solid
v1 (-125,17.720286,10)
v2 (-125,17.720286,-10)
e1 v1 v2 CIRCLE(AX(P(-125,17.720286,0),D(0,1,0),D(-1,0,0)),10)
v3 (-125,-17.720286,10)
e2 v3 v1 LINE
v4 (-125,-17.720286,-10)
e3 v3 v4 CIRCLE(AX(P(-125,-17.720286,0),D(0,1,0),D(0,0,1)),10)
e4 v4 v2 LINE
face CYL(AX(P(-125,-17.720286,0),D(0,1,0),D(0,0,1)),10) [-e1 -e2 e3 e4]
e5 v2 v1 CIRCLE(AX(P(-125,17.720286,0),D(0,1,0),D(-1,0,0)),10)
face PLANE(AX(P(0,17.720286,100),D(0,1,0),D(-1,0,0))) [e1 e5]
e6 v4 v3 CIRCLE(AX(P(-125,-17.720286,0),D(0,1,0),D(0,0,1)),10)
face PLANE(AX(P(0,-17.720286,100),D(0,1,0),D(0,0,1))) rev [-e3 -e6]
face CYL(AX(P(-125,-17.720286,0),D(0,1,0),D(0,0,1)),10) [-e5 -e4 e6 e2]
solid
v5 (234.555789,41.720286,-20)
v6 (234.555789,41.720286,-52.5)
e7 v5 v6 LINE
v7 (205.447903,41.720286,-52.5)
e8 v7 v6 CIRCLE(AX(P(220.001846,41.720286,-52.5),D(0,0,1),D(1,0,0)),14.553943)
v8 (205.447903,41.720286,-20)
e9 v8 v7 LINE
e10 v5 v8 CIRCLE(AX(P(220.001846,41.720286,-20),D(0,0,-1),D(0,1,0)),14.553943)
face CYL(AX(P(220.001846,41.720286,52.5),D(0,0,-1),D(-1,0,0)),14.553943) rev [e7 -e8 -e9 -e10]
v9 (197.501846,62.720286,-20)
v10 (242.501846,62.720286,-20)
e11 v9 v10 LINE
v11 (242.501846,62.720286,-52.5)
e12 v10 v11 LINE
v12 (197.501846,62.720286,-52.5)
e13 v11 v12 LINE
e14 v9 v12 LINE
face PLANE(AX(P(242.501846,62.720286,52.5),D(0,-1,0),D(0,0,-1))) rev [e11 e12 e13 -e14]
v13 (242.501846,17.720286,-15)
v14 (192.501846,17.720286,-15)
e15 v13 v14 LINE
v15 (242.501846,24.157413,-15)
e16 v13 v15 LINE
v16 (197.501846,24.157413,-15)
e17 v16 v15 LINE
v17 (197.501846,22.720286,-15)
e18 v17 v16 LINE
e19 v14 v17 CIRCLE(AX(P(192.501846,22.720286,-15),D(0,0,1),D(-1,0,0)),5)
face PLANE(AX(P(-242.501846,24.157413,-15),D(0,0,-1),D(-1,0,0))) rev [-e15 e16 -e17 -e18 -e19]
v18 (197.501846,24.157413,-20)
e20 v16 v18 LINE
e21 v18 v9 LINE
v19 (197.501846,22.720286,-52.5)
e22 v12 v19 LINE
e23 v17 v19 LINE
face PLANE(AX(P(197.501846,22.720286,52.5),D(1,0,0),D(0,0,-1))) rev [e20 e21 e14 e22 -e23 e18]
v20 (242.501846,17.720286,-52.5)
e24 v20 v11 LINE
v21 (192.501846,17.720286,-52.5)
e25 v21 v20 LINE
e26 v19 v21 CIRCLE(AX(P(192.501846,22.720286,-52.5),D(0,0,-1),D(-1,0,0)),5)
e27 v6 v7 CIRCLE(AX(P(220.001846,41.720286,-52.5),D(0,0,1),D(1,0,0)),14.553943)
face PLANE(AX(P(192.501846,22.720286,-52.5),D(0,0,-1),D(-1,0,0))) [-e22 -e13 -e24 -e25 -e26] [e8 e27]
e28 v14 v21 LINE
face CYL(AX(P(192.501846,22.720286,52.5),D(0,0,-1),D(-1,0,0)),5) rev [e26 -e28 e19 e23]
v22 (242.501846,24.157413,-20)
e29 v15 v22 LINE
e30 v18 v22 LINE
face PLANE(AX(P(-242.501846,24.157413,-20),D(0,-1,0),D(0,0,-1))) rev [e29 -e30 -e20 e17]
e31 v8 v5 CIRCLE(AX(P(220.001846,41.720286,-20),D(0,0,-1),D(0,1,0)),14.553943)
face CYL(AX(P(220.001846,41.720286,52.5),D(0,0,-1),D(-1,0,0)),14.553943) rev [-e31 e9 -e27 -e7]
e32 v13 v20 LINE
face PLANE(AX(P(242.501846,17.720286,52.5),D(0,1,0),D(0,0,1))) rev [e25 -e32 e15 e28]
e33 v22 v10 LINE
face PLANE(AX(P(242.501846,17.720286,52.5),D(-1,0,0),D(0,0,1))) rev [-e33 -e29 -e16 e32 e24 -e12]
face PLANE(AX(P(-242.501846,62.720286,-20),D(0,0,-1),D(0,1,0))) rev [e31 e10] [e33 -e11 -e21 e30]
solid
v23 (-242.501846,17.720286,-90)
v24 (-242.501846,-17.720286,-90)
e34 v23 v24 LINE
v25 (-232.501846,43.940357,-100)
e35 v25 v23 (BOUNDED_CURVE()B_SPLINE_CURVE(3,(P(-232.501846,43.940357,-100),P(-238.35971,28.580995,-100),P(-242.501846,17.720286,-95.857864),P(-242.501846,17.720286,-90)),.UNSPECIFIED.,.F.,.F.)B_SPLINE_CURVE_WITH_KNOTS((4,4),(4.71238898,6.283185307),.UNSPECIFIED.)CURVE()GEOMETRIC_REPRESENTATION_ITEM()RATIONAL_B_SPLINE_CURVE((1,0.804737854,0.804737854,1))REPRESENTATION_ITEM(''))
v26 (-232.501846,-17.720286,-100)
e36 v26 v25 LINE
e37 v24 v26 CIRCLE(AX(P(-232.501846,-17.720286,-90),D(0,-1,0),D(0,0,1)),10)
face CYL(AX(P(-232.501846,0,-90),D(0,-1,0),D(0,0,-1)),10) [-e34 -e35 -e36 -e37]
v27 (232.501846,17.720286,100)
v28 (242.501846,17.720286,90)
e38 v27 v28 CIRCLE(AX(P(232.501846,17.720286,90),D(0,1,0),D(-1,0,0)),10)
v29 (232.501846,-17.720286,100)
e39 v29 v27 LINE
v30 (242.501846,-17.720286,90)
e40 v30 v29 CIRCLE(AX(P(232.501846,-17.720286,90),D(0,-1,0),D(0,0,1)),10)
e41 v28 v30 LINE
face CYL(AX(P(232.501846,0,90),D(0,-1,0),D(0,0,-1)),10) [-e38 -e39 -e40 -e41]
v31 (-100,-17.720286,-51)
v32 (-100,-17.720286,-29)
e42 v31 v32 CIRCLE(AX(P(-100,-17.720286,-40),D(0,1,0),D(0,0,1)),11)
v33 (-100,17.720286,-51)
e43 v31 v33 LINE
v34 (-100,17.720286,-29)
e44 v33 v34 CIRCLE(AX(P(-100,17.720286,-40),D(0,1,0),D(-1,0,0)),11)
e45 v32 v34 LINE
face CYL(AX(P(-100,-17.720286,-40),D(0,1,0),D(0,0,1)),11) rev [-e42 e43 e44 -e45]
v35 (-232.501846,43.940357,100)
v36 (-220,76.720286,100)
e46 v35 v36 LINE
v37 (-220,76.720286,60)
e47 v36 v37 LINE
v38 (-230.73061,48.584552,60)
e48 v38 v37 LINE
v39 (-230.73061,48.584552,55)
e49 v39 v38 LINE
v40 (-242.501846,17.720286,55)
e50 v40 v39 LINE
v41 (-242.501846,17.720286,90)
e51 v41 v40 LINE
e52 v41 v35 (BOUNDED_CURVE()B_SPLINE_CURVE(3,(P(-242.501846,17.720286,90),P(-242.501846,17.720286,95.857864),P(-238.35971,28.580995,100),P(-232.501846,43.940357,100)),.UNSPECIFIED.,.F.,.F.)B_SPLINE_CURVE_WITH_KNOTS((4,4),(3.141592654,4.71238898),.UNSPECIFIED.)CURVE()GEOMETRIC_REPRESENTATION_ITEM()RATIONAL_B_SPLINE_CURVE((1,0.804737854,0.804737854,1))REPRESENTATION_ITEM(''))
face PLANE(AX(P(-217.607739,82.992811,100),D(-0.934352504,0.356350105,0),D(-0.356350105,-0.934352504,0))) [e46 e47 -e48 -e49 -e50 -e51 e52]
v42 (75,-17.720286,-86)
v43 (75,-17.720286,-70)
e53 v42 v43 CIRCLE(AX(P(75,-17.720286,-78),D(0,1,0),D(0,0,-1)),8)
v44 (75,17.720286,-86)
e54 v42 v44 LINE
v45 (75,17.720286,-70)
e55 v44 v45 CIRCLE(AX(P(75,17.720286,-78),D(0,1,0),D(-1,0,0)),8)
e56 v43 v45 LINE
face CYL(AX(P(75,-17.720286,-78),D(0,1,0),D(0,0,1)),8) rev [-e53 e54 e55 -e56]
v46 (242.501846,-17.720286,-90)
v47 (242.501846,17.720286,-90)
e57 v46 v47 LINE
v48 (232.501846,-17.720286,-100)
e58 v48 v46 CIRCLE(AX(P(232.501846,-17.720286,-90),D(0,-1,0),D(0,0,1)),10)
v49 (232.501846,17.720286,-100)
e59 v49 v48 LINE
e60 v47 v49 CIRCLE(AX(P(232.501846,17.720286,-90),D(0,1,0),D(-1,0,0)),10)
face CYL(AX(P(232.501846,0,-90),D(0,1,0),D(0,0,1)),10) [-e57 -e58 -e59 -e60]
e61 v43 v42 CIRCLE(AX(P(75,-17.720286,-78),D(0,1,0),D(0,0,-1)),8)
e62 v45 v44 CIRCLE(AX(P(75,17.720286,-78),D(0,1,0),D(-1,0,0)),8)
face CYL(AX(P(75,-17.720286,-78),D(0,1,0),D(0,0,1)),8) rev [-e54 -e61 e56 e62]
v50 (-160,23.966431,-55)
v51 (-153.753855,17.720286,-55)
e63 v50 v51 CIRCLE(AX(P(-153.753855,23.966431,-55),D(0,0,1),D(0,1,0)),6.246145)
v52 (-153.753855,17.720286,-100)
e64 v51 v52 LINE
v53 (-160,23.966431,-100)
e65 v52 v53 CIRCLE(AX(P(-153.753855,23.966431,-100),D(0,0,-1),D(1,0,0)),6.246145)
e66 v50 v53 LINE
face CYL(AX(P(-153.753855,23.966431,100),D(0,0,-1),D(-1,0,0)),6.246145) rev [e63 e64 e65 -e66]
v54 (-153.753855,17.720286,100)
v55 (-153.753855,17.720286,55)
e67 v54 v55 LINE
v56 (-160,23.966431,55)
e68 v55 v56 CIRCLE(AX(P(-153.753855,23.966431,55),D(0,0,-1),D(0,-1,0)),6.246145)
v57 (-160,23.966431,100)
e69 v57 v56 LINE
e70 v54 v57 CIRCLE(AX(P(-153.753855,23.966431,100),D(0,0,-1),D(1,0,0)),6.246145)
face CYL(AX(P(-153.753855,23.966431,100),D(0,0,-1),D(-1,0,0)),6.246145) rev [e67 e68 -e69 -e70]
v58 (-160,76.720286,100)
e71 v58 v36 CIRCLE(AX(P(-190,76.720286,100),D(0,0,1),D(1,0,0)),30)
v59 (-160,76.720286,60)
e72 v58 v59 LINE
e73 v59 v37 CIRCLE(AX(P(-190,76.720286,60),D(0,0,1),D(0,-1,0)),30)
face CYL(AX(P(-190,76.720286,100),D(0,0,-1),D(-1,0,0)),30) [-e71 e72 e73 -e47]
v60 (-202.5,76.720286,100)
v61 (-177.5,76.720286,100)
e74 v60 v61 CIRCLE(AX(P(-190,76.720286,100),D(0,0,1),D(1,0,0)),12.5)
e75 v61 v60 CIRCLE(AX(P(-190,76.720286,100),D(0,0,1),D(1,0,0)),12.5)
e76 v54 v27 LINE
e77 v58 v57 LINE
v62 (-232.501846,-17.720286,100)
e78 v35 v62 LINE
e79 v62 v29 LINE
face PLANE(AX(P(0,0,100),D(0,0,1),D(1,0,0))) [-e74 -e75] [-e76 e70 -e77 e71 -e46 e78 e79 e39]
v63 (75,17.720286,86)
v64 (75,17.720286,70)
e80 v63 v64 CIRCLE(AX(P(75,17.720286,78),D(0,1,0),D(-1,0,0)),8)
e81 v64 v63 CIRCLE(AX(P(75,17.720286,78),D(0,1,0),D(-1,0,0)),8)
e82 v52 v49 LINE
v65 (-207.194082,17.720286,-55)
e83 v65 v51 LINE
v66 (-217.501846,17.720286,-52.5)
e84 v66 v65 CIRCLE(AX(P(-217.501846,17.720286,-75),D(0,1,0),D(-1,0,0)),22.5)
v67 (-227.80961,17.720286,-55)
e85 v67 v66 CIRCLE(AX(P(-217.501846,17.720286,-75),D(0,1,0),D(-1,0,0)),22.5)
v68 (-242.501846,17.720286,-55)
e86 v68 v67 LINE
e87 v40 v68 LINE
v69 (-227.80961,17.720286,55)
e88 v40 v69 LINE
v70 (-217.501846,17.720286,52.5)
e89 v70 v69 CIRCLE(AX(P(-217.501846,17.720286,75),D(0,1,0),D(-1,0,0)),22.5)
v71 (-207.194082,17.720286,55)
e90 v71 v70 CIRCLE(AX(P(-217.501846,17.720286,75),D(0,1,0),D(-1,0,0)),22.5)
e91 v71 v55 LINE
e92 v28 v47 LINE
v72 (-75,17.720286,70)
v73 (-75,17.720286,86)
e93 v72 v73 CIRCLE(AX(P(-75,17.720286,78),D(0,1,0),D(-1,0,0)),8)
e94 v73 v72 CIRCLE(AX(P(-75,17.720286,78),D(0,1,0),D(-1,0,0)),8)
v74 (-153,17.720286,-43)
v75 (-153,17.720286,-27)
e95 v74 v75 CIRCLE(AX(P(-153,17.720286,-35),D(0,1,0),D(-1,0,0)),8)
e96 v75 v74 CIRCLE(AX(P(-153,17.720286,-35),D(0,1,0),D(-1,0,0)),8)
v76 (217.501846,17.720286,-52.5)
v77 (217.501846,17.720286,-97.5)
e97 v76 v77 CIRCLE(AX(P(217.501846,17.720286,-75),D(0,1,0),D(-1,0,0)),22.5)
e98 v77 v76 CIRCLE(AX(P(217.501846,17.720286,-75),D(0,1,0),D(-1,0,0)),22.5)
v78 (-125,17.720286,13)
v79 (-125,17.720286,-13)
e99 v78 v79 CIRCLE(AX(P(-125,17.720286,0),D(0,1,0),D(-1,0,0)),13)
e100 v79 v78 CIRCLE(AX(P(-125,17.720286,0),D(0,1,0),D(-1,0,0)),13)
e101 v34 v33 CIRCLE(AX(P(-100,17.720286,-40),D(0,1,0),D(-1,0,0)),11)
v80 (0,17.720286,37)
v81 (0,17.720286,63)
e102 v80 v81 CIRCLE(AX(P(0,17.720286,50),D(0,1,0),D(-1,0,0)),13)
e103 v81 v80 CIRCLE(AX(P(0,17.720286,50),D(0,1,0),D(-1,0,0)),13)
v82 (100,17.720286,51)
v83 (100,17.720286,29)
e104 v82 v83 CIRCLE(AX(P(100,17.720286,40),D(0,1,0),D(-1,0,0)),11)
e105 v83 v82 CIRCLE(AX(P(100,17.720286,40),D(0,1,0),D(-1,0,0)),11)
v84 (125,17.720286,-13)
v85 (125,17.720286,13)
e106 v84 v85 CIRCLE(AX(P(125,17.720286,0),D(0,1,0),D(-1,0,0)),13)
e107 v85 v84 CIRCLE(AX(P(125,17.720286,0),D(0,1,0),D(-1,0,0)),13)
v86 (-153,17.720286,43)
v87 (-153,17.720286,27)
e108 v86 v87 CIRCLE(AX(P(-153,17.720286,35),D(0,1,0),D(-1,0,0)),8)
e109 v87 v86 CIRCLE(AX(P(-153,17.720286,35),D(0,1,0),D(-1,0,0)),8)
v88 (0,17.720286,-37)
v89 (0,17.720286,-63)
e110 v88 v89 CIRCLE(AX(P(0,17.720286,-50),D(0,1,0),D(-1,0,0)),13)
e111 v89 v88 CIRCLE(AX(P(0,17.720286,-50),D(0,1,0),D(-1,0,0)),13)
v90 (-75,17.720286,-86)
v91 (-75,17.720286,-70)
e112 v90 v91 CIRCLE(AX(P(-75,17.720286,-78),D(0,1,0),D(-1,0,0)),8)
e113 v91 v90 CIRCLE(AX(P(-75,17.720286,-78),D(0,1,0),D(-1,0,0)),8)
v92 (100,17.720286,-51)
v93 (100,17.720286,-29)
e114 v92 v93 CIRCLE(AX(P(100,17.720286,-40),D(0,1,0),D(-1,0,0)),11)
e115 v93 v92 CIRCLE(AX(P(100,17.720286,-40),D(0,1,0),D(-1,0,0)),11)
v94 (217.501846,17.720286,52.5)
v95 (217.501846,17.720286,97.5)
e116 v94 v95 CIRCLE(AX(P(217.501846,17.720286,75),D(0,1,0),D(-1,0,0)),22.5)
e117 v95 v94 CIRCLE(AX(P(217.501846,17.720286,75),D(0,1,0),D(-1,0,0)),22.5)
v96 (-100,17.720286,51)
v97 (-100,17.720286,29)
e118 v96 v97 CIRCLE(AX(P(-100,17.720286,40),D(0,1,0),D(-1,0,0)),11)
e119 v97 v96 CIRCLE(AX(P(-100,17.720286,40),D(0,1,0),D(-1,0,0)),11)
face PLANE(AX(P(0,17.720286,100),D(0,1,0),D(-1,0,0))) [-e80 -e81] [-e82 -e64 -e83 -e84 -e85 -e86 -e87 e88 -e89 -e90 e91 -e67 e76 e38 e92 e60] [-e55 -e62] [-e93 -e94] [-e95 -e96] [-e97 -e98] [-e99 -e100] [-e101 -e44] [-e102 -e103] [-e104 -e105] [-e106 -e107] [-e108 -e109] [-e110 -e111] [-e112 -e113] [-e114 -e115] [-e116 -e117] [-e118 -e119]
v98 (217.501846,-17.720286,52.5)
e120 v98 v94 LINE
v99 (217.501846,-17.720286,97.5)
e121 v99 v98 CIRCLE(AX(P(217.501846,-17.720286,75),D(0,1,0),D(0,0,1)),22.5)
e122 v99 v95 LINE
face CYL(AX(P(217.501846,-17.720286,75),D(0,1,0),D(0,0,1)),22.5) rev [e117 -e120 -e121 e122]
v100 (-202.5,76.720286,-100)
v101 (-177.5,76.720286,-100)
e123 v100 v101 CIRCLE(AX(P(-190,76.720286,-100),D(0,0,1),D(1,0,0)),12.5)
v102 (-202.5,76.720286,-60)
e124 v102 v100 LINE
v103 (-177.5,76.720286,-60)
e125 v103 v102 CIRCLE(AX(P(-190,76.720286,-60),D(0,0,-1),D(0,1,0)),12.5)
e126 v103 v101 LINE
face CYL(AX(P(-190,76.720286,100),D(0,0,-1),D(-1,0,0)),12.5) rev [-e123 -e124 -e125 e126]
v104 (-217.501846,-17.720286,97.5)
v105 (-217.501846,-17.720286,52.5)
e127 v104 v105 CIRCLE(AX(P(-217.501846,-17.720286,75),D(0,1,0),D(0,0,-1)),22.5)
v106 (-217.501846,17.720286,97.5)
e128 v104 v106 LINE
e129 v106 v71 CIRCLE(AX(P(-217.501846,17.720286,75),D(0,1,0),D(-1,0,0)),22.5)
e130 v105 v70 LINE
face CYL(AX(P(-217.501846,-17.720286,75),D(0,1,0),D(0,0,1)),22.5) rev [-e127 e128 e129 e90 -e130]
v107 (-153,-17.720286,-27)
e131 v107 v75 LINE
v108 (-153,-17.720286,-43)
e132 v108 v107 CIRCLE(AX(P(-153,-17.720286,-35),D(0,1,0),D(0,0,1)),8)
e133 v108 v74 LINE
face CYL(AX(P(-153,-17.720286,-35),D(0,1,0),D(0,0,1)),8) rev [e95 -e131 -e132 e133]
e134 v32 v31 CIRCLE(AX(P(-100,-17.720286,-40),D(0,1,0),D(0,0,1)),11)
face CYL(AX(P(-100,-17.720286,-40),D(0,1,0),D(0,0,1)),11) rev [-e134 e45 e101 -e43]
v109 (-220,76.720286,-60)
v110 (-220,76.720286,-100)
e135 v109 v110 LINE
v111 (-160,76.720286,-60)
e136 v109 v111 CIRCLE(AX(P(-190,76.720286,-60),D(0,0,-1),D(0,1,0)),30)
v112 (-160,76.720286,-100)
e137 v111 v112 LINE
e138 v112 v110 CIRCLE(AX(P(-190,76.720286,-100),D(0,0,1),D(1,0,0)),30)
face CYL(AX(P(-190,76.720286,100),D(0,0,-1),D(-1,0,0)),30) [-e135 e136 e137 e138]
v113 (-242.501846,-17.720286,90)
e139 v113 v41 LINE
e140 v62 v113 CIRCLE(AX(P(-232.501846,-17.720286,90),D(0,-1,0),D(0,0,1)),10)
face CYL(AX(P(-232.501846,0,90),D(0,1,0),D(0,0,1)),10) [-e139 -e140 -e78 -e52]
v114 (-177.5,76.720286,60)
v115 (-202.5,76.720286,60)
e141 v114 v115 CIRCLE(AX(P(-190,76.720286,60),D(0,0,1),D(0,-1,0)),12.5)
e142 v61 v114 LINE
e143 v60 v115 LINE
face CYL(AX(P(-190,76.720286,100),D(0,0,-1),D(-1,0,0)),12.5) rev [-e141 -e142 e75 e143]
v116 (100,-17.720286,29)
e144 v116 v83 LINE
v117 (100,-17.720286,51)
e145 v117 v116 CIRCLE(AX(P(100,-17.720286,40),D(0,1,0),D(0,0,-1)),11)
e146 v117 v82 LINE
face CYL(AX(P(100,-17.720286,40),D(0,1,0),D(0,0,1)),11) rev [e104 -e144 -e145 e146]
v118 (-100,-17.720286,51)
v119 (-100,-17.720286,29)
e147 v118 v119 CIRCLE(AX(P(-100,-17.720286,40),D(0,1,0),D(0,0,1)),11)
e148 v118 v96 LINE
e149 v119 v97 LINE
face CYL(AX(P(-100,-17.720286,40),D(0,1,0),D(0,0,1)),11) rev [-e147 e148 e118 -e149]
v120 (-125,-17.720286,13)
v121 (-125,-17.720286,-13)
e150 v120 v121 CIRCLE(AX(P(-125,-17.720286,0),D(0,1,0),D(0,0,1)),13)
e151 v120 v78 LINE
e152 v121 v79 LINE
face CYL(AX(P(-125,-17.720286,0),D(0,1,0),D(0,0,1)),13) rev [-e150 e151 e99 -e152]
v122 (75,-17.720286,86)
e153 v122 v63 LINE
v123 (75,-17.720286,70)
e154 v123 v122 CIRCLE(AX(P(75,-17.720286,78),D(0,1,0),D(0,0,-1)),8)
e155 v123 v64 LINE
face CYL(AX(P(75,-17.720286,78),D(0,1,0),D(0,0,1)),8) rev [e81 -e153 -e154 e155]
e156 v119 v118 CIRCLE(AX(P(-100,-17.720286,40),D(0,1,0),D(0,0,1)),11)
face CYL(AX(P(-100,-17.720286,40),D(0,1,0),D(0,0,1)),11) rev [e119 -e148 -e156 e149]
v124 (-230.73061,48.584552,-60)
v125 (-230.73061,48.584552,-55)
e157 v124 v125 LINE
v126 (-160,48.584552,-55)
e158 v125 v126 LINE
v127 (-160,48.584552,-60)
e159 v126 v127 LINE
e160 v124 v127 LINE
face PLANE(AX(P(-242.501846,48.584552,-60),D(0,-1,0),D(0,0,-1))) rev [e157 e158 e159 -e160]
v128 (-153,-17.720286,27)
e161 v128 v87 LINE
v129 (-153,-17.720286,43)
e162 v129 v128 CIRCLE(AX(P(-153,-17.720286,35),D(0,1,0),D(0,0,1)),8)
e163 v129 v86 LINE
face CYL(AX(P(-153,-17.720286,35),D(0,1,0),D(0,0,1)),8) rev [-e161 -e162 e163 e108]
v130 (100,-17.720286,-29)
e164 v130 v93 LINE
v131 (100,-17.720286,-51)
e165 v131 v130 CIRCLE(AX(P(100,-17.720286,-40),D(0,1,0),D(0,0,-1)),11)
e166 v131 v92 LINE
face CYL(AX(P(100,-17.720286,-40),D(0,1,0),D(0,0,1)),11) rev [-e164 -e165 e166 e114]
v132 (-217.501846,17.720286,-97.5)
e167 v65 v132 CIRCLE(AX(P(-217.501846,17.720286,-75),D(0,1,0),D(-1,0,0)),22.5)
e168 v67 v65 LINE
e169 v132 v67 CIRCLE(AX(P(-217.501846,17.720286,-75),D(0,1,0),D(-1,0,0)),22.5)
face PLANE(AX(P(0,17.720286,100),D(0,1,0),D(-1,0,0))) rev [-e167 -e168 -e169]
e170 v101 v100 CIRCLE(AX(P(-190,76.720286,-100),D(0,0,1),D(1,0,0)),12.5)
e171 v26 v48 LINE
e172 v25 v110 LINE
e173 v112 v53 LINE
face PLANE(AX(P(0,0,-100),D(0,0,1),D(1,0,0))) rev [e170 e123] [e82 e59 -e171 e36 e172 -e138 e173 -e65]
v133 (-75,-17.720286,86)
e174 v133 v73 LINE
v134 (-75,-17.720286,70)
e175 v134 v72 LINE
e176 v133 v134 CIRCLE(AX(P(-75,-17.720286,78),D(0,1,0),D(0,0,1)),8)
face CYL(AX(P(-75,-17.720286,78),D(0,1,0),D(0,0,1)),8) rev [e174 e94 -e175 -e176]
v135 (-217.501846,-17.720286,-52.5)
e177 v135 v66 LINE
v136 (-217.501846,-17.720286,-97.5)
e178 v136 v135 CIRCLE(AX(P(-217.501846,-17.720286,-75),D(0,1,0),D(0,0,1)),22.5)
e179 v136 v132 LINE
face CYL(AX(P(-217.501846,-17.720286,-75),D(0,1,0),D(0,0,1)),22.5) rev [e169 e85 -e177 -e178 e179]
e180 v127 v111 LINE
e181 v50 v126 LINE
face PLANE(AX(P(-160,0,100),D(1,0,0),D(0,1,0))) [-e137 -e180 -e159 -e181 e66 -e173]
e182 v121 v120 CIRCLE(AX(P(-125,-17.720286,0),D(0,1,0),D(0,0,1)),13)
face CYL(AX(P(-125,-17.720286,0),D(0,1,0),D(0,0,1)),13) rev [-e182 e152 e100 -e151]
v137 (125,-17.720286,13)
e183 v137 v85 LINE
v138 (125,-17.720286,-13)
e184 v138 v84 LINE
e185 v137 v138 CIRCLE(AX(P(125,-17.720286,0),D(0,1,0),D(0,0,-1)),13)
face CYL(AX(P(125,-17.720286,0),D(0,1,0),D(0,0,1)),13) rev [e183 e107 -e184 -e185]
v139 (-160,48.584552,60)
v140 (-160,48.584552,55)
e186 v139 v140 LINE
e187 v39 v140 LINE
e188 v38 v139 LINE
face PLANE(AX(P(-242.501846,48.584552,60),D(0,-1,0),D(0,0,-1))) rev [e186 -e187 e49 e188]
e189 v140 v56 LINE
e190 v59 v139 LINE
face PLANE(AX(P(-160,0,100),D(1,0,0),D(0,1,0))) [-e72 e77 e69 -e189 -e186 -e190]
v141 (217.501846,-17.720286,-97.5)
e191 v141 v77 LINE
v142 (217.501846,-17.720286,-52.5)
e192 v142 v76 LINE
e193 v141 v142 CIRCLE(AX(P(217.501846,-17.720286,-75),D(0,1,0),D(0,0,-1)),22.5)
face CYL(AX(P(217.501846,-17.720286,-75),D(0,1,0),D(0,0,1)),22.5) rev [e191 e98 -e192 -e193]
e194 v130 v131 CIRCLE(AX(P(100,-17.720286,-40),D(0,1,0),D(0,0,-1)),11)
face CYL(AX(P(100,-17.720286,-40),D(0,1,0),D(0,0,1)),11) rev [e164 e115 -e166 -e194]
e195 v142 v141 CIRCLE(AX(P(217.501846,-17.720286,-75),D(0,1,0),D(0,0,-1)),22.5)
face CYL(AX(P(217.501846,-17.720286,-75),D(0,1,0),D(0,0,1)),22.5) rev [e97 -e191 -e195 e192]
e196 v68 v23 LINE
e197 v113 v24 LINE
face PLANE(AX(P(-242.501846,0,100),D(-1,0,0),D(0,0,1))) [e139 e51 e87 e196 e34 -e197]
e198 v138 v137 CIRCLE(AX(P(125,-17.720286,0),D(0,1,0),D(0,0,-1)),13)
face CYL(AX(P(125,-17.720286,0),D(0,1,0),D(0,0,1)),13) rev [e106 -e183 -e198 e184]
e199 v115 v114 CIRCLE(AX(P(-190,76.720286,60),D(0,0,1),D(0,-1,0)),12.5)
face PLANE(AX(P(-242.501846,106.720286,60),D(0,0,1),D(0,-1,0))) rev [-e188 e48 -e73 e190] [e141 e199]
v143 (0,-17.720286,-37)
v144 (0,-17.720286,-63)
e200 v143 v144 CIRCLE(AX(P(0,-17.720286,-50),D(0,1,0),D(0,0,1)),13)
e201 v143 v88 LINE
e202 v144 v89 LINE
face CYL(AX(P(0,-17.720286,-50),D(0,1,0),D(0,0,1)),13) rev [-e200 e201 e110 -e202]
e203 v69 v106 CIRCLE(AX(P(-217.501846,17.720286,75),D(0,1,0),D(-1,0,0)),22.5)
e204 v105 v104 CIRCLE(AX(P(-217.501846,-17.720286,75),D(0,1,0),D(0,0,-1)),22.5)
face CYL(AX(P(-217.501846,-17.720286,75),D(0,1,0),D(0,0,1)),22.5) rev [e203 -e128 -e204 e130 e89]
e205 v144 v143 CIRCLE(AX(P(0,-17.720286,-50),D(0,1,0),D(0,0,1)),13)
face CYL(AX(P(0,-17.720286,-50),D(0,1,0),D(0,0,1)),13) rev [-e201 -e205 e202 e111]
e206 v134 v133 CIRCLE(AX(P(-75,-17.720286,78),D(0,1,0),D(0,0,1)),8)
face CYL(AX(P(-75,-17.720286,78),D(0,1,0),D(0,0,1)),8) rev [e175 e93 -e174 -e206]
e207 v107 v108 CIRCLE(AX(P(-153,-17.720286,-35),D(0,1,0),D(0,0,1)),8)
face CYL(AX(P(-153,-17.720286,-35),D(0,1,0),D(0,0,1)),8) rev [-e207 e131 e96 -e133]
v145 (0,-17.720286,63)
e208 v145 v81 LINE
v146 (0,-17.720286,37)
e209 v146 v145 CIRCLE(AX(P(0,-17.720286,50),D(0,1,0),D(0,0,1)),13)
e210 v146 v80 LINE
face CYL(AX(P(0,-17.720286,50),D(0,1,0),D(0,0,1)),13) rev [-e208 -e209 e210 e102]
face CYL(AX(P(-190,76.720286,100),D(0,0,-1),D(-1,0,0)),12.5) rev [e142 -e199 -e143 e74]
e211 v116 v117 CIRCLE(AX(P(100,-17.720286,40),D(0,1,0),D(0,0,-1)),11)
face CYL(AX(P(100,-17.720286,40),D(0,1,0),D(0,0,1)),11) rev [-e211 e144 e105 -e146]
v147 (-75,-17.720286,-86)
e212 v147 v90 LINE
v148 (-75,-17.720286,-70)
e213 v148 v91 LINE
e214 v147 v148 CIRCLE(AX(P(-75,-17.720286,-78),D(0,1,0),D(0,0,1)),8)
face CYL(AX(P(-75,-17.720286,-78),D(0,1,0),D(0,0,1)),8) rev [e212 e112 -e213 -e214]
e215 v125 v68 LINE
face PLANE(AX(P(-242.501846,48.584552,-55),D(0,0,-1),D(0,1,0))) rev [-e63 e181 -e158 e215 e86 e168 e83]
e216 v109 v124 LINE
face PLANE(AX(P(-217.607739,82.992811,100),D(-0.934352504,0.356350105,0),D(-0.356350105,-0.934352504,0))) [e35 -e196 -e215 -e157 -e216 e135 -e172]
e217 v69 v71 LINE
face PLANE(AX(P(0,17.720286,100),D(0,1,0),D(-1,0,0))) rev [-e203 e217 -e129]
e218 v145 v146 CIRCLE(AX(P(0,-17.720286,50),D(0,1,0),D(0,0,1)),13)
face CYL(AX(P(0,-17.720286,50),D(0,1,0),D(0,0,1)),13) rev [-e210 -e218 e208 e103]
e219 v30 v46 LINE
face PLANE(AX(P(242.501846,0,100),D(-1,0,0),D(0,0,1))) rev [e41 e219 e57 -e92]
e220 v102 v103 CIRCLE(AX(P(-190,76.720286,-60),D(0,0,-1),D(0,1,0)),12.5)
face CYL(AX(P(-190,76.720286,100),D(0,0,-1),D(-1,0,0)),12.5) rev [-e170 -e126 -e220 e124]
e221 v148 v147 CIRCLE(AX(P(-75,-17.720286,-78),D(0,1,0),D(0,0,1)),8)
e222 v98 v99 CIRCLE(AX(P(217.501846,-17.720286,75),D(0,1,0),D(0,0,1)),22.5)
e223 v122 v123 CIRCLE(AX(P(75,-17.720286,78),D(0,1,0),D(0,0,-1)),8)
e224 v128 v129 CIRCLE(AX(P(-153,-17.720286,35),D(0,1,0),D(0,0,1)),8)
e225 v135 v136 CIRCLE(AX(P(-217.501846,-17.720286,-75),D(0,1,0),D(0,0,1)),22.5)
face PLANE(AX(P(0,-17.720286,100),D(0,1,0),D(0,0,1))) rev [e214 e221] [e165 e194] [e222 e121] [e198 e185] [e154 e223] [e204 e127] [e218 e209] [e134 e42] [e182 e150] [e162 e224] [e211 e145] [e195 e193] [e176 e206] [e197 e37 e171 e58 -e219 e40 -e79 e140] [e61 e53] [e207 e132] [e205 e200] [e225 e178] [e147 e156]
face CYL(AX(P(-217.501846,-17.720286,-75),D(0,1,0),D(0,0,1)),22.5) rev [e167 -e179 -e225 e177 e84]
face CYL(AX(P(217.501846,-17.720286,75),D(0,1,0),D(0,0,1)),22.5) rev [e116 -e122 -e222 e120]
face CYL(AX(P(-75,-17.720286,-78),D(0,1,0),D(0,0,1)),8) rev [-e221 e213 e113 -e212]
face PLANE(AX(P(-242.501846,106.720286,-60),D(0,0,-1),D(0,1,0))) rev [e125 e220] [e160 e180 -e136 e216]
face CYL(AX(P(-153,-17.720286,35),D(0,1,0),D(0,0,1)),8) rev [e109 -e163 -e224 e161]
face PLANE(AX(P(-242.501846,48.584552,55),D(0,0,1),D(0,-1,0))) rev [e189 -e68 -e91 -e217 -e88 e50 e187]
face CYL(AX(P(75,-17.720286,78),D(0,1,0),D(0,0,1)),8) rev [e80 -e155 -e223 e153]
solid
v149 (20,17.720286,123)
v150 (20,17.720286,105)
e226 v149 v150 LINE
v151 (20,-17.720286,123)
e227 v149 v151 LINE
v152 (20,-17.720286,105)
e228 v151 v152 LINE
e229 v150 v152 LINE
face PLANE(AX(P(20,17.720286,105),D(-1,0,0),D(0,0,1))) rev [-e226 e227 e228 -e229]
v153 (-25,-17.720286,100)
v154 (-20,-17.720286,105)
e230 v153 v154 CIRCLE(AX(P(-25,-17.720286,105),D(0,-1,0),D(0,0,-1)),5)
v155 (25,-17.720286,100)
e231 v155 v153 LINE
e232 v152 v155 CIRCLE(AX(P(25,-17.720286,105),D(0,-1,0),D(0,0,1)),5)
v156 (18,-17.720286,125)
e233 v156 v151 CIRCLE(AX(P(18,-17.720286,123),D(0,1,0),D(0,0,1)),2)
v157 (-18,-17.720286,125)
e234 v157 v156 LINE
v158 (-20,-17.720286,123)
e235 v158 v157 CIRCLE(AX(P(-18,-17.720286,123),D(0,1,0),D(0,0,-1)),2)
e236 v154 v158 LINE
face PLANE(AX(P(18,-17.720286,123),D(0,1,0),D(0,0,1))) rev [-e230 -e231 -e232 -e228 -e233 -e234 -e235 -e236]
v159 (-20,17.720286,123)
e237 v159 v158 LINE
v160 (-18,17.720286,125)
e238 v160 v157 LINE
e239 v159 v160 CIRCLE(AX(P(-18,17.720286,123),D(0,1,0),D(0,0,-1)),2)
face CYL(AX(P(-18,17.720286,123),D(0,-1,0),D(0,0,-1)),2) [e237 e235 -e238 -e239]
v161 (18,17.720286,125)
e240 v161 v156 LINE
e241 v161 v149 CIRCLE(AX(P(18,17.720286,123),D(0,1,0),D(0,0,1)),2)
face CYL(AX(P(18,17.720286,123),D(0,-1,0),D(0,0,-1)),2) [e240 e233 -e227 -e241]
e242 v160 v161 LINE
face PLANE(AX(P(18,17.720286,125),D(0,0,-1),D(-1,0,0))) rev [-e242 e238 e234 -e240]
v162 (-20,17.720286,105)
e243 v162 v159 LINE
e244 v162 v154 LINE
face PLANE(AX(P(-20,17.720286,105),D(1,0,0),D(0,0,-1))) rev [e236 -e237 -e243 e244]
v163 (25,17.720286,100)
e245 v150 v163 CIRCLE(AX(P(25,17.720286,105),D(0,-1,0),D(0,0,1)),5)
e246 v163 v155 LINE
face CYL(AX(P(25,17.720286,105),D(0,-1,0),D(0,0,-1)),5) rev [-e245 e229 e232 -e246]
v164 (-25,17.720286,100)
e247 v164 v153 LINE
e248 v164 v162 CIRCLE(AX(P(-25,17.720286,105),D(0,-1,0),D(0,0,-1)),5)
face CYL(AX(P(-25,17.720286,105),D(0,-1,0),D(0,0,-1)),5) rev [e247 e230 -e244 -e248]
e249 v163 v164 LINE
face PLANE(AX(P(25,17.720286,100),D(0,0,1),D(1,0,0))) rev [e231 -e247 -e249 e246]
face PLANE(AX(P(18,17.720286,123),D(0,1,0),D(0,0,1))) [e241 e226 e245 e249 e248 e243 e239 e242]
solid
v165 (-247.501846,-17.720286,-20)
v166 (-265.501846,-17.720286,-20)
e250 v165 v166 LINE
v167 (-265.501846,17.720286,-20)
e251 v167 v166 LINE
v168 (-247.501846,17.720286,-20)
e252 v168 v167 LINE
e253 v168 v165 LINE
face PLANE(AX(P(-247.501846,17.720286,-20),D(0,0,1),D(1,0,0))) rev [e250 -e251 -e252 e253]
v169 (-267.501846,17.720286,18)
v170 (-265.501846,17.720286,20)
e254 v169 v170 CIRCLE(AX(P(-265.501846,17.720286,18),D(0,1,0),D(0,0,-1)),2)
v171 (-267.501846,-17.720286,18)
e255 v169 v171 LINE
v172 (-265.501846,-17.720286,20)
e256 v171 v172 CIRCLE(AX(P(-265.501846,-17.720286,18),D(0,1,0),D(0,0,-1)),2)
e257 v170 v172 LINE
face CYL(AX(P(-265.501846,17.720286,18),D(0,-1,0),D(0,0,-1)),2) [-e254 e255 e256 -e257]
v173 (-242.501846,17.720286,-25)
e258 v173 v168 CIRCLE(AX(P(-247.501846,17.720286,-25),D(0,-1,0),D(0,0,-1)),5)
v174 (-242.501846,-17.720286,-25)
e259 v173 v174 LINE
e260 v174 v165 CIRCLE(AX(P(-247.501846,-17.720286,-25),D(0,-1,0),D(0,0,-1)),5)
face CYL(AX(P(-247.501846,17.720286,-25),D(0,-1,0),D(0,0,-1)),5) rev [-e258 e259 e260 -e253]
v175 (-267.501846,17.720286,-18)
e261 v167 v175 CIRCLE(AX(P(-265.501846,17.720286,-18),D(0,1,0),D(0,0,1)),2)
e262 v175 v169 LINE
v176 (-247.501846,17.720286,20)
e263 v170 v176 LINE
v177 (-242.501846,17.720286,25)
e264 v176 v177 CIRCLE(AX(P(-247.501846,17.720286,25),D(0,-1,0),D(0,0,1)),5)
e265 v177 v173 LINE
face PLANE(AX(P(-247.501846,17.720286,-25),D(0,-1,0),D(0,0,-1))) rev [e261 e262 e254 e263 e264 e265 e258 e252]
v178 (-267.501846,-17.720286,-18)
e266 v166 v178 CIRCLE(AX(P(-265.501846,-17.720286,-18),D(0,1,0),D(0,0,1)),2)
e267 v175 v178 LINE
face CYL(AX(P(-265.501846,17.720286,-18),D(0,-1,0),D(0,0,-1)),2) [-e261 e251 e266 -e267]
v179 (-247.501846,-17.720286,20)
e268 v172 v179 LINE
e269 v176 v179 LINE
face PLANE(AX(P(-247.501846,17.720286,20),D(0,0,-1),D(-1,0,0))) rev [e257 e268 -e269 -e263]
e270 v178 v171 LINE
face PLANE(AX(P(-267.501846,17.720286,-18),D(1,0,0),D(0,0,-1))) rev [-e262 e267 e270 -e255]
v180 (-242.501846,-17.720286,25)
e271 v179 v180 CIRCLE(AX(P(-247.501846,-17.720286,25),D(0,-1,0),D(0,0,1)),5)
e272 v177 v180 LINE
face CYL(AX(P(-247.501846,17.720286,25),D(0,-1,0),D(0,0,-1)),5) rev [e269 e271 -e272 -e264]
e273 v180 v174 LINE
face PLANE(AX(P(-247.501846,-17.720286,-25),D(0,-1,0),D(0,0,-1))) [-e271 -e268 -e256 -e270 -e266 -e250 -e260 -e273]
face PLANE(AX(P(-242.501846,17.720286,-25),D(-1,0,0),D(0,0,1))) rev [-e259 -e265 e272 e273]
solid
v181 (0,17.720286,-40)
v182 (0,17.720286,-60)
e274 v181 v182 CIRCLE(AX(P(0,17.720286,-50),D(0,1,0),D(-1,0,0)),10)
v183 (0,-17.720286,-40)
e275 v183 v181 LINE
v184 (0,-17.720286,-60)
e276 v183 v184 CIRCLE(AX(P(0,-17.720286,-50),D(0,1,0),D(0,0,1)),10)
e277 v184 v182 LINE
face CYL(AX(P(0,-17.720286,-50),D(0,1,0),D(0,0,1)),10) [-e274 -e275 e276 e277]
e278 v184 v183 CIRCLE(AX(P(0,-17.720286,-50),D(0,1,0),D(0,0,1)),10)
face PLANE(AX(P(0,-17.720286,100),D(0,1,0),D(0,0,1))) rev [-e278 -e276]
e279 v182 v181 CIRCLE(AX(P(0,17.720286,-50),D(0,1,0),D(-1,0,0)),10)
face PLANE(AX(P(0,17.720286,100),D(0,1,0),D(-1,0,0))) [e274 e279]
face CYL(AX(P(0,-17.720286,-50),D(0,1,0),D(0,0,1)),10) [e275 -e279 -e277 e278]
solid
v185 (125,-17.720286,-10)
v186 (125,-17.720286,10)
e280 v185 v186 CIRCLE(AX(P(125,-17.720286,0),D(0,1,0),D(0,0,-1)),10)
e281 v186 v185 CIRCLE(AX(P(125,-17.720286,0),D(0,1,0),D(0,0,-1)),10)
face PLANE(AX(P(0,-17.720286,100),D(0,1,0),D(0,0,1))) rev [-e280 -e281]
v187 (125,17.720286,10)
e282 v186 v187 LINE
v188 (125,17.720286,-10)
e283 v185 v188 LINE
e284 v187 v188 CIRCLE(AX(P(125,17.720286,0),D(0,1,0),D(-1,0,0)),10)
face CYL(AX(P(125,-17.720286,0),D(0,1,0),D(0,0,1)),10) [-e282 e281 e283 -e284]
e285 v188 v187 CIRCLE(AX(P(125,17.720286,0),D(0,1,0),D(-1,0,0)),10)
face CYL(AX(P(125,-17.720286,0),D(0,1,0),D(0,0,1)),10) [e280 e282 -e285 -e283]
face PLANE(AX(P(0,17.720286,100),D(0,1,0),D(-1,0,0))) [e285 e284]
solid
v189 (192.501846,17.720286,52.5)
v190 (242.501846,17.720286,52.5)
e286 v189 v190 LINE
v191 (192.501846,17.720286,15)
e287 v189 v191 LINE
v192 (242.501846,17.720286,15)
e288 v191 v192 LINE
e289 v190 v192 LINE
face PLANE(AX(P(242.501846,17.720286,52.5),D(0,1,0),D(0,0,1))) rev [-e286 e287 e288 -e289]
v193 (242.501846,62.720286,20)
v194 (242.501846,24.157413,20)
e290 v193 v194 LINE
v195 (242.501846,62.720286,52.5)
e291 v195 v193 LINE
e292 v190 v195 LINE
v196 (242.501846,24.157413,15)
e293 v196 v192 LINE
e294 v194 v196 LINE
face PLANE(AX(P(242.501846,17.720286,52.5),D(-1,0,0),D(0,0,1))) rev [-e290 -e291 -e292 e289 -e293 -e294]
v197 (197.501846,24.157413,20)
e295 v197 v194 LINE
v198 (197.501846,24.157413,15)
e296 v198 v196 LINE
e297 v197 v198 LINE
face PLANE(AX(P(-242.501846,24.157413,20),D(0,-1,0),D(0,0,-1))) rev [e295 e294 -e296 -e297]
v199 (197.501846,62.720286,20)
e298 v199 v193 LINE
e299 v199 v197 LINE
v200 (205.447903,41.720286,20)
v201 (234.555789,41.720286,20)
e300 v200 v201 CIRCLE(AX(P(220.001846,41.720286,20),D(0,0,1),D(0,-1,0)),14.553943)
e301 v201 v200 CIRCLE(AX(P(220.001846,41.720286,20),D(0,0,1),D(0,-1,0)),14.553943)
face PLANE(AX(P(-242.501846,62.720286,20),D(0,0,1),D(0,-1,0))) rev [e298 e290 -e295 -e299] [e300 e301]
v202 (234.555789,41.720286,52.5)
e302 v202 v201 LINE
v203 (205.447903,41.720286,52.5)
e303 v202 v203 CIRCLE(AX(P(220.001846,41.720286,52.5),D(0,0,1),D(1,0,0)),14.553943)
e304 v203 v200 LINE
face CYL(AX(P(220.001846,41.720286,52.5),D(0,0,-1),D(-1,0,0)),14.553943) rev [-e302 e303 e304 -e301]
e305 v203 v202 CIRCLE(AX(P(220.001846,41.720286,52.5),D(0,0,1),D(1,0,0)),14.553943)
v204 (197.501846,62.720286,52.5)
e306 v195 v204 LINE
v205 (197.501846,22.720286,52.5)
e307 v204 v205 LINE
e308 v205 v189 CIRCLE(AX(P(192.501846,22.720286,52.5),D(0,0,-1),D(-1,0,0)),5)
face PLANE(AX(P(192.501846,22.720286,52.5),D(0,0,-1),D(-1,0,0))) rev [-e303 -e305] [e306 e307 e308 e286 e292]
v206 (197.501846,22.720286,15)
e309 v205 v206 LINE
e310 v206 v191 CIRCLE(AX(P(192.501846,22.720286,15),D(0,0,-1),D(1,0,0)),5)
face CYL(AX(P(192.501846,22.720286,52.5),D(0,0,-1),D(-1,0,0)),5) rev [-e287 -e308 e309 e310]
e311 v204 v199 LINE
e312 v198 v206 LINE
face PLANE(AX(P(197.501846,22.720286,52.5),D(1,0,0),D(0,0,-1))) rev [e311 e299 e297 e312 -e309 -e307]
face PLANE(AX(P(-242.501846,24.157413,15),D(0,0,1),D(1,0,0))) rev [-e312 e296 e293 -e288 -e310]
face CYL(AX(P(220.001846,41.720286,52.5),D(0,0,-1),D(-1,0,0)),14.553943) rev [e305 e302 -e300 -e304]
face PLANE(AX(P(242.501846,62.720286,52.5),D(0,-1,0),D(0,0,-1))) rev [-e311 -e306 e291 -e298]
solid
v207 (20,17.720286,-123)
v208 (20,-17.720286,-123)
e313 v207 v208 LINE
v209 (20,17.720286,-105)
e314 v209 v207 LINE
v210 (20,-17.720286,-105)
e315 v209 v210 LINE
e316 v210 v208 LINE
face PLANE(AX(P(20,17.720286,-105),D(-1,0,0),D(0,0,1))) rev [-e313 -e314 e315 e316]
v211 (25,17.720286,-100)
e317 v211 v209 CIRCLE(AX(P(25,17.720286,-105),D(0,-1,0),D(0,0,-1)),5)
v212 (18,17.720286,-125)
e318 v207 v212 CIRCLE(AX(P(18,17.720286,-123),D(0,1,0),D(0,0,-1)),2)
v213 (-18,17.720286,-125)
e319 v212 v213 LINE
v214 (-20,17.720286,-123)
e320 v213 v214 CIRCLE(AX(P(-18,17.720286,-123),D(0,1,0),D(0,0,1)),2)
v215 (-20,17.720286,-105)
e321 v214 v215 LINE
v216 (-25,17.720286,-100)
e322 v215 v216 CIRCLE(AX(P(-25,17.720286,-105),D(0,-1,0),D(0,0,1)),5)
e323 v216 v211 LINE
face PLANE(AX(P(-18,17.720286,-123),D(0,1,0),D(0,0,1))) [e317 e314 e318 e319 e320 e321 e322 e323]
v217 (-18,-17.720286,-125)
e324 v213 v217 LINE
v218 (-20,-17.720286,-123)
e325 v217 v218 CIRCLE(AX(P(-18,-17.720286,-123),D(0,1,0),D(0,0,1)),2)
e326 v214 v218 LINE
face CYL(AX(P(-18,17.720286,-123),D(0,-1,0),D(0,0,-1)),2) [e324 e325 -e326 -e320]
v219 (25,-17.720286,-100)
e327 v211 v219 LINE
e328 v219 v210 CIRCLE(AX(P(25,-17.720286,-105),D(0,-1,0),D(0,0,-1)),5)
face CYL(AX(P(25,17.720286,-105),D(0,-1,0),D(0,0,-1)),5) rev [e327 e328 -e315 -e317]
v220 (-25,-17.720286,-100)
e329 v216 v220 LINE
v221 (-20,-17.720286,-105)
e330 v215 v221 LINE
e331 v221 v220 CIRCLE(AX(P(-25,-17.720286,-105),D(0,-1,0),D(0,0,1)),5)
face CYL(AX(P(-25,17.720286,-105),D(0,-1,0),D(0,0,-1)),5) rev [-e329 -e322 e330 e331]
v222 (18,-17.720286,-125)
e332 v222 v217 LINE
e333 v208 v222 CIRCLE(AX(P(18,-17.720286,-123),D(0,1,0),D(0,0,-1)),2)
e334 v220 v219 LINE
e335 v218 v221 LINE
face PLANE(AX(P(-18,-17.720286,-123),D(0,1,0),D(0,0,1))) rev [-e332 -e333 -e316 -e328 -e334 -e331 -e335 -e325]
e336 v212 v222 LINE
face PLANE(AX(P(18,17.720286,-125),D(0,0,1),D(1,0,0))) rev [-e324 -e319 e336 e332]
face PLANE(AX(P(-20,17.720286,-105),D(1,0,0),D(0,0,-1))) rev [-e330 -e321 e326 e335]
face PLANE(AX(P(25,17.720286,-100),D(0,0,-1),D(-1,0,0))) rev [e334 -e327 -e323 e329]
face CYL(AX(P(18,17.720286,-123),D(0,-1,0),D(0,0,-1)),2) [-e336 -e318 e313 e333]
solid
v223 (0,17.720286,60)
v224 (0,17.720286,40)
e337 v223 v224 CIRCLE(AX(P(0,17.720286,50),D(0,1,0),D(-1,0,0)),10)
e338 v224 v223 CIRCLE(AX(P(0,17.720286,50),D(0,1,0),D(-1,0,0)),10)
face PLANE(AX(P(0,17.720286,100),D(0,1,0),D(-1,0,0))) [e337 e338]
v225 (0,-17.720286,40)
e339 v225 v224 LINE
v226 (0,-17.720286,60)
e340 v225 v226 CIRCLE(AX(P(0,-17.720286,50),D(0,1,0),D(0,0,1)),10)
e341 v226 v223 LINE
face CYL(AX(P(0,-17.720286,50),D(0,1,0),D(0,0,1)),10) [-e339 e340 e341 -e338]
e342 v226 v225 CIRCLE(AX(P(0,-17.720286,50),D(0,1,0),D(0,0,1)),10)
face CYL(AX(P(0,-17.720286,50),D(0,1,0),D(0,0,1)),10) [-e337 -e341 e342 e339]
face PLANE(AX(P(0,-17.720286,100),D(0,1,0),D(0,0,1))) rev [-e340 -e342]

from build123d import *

# Parameters (mm, degrees)
SKETCH1_R                  = 12.5
BOSS_EXTRUDE1_DEPTH        = 100
CUT_EXTRUDE1_DEPTH         = 284.18962695
CUT_EXTRUDE1_DEPTH_BACK    = 284.18962695
SKETCH3_R                  = 14.553943417
BOSS_EXTRUDE2_DEPTH        = 52.5
CUT_EXTRUDE3_DEPTH         = 284.18962695
CUT_EXTRUDE3_DEPTH_BACK    = 284.18962695
CUT_EXTRUDE4_DEPTH         = 284.18962695
CUT_EXTRUDE4_DEPTH_BACK    = 284.18962695
SKETCH5_R                  = 8
SKETCH5_R_2                = 13
SKETCH5_R_3                = 10
SKETCH5_R_4                = 11
SKETCH5_W                  = 20.521758455
SKETCH5_H                  = 25
BOSS_EXTRUDE5_DEPTH        = 17.720286
BOSS_EXTRUDE5_DEPTH_BACK   = 17.720286
BOSS_EXTRUDE5_2_DEPTH      = 17.720286
BOSS_EXTRUDE5_2_DEPTH_BACK = 17.720286
BOSS_EXTRUDE5_3_DEPTH      = 17.720286
BOSS_EXTRUDE5_3_DEPTH_BACK = 17.720286
CUT_EXTRUDE5_DEPTH         = 17.720286
CUT_EXTRUDE5_DEPTH_BACK    = 314.960916539
SKETCH7_R                  = 22.5
FILLET11_R                 = 10


with BuildPart() as part:
    # Sketch1 → Boss-Extrude1 (new, symmetric)
    # profile 1 of 2: a face of its own
    with BuildSketch(Plane.XY):
        with BuildLine():
            Line((-231.799247234, 17.720286162), (-231.799247234, -17.720286162))
            Line((-231.799247234, -17.720286162), (242.501846041, -17.720286162))
            Line((242.501846041, -17.720286162), (242.501846041, 17.720286162))
            Line((242.501846041, 17.720286162), (-153.753855421, 17.720286162))
            ThreePointArc((-153.753855421, 17.720286162), (-158.170546609, 19.549739553), (-160, 23.966430741))
            Line((-160, 23.966430741), (-160, 76.720286162))
            ThreePointArc((-160, 76.720286162), (-190, 106.720286162), (-220, 76.720286162))
            ThreePointArc((-220, 76.720286162), (-218.824763602, 68.405660295), (-215.391133112, 60.742477825))
            Line((-215.391133112, 60.742477825), (-231.799247234, 17.720286162))
        make_face()
        with Locations((-190, 76.720286162)):
            Circle(SKETCH1_R, mode=Mode.SUBTRACT)
    # profile 2 of 2: a face of its own
    with BuildSketch(Plane.XY):
        with BuildLine():
            Line((-242.501846041, -17.279713838), (-242.501846041, -17.720286162))
            Line((-242.501846041, -17.720286162), (-231.799247234, -17.720286162))
            Line((-231.799247234, -17.720286162), (-231.799247234, 17.720286162))
            Line((-231.799247234, 17.720286162), (-215.391133112, 60.742477825))
            ThreePointArc((-215.391133112, 60.742477825), (-218.824763602, 68.405660295), (-220, 76.720286162))
            Line((-220, 76.720286162), (-242.501846041, 17.720286162))
            Line((-242.501846041, 17.720286162), (-242.501846041, -17.279713838))
        make_face()
    extrude(amount=BOSS_EXTRUDE1_DEPTH, both=True)

    # Sketch2 → Cut-Extrude1 (cut, two sides: drawn at the far end of the back side and taken through both)
    with BuildSketch(Plane(origin=(0, 0, 0), x_dir=(0, 0, -1), z_dir=(1, 0, 0)).offset(-CUT_EXTRUDE1_DEPTH_BACK)):
        Polygon((-60, 106.720286162), (-60, 48.584551896), (-55, 48.584551896), (-55, 17.720286162), (55, 17.720286162), (55, 48.584551896), (60, 48.584551896), (60, 106.720286162), align=None)
    extrude(amount=CUT_EXTRUDE1_DEPTH + CUT_EXTRUDE1_DEPTH_BACK, mode=Mode.SUBTRACT)

    # Sketch5 → Cut-Extrude4 (cut, two sides: drawn at the far end of the back side and taken through both)
    # profile 1 of 15: a face of its own
    with BuildSketch(Plane(origin=(0, 0, 0), x_dir=(1, 0, 0), z_dir=(0, 1, 0)).offset(-CUT_EXTRUDE4_DEPTH_BACK)):
        with Locations(Location((-153, 35, 0), (0, 0, 270))):
            Circle(SKETCH5_R)
    # profile 2 of 15: a face of its own
    with BuildSketch(Plane(origin=(0, 0, 0), x_dir=(1, 0, 0), z_dir=(0, 1, 0)).offset(-CUT_EXTRUDE4_DEPTH_BACK)):
        with Locations(Location((-153, -35, 0), (0, 0, 270))):
            Circle(SKETCH5_R)
    # profile 3 of 15: a face of its own
    with BuildSketch(Plane(origin=(0, 0, 0), x_dir=(1, 0, 0), z_dir=(0, 1, 0)).offset(-CUT_EXTRUDE4_DEPTH_BACK)):
        with Locations(Location((-125, 0, 0), (0, 0, 270))):
            Circle(SKETCH5_R_2)
        with Locations(Location((-125, 0, 0), (0, 0, 270))):
            Circle(SKETCH5_R_3, mode=Mode.SUBTRACT)
    # profile 4 of 15: a face of its own
    with BuildSketch(Plane(origin=(0, 0, 0), x_dir=(1, 0, 0), z_dir=(0, 1, 0)).offset(-CUT_EXTRUDE4_DEPTH_BACK)):
        with Locations(Location((-100, 40, 0), (0, 0, 270))):
            Circle(SKETCH5_R_4)
    # profile 5 of 15: a face of its own
    with BuildSketch(Plane(origin=(0, 0, 0), x_dir=(1, 0, 0), z_dir=(0, 1, 0)).offset(-CUT_EXTRUDE4_DEPTH_BACK)):
        with Locations(Location((-100, -40, 0), (0, 0, 270))):
            Circle(SKETCH5_R_4)
    # profile 6 of 15: a face of its own
    with BuildSketch(Plane(origin=(0, 0, 0), x_dir=(1, 0, 0), z_dir=(0, 1, 0)).offset(-CUT_EXTRUDE4_DEPTH_BACK)):
        with Locations(Location((0, 50, 0), (0, 0, 270))):
            Circle(SKETCH5_R_2)
        with Locations(Location((0, 50, 0), (0, 0, 270))):
            Circle(SKETCH5_R_3, mode=Mode.SUBTRACT)
    # profile 7 of 15: a face of its own
    with BuildSketch(Plane(origin=(0, 0, 0), x_dir=(1, 0, 0), z_dir=(0, 1, 0)).offset(-CUT_EXTRUDE4_DEPTH_BACK)):
        with Locations(Location((0, -50, 0), (0, 0, 270))):
            Circle(SKETCH5_R_2)
        with Locations(Location((0, -50, 0), (0, 0, 270))):
            Circle(SKETCH5_R_3, mode=Mode.SUBTRACT)
    # profile 8 of 15: a face of its own
    with BuildSketch(Plane(origin=(0, 0, 0), x_dir=(1, 0, 0), z_dir=(0, 1, 0)).offset(-CUT_EXTRUDE4_DEPTH_BACK)):
        with Locations(Location((75, -78, 0), (0, 0, 180))):
            Circle(SKETCH5_R)
    # profile 9 of 15: a face of its own
    with BuildSketch(Plane(origin=(0, 0, 0), x_dir=(1, 0, 0), z_dir=(0, 1, 0)).offset(-CUT_EXTRUDE4_DEPTH_BACK)):
        with Locations(Location((100, -40, 0), (0, 0, 180))):
            Circle(SKETCH5_R_4)
    # profile 10 of 15: a face of its own
    with BuildSketch(Plane(origin=(0, 0, 0), x_dir=(1, 0, 0), z_dir=(0, 1, 0)).offset(-CUT_EXTRUDE4_DEPTH_BACK)):
        with Locations(Location((-75, 78, 0), (0, 0, 270))):
            Circle(SKETCH5_R)
    # profile 11 of 15: a face of its own
    with BuildSketch(Plane(origin=(0, 0, 0), x_dir=(1, 0, 0), z_dir=(0, 1, 0)).offset(-CUT_EXTRUDE4_DEPTH_BACK)):
        with Locations(Location((-75, -78, 0), (0, 0, 270))):
            Circle(SKETCH5_R)
    # profile 12 of 15: a face of its own
    with BuildSketch(Plane(origin=(0, 0, 0), x_dir=(1, 0, 0), z_dir=(0, 1, 0)).offset(-CUT_EXTRUDE4_DEPTH_BACK)):
        with Locations(Location((125, 0, 0), (0, 0, 180))):
            Circle(SKETCH5_R_2)
        with Locations(Location((125, 0, 0), (0, 0, 180))):
            Circle(SKETCH5_R_3, mode=Mode.SUBTRACT)
    # profile 13 of 15: a face of its own
    with BuildSketch(Plane(origin=(0, 0, 0), x_dir=(1, 0, 0), z_dir=(0, 1, 0)).offset(-CUT_EXTRUDE4_DEPTH_BACK)):
        with Locations(Location((100, 40, 0), (0, 0, 180))):
            Circle(SKETCH5_R_4)
    # profile 14 of 15: a face of its own
    with BuildSketch(Plane(origin=(0, 0, 0), x_dir=(1, 0, 0), z_dir=(0, 1, 0)).offset(-CUT_EXTRUDE4_DEPTH_BACK)):
        with Locations(Location((75, 78, 0), (0, 0, 180))):
            Circle(SKETCH5_R)
    # profile 15 of 15: a face of its own
    with BuildSketch(Plane(origin=(0, 0, 0), x_dir=(1, 0, 0), z_dir=(0, 1, 0)).offset(-CUT_EXTRUDE4_DEPTH_BACK)):
        with Locations((-10.260879228, 112.5)):
            Rectangle(SKETCH5_W, SKETCH5_H)
    extrude(amount=CUT_EXTRUDE4_DEPTH + CUT_EXTRUDE4_DEPTH_BACK, mode=Mode.SUBTRACT)


with BuildPart() as body_2:
    # Sketch3 → Boss-Extrude2 (new, symmetric)
    with BuildSketch(Plane.XY):
        with BuildLine():
            Line((242.501846041, 17.720286162), (192.501846041, 17.720286162))
            ThreePointArc((192.501846041, 17.720286162), (196.037379947, 19.184752256), (197.501846041, 22.720286162))
            Line((197.501846041, 22.720286162), (197.501846041, 62.720286162))
            Line((197.501846041, 62.720286162), (242.501846041, 62.720286162))
            Line((242.501846041, 62.720286162), (242.501846041, 17.720286162))
        make_face()
        with Locations((220.001846041, 41.720286162)):
            Circle(SKETCH3_R, mode=Mode.SUBTRACT)
    extrude(amount=BOSS_EXTRUDE2_DEPTH, both=True)

    # Sketch4 → Cut-Extrude3 (cut, two sides: drawn at the far end of the back side and taken through both)
    with BuildSketch(Plane(origin=(0, 0, 0), x_dir=(0, 0, -1), z_dir=(1, 0, 0)).offset(-CUT_EXTRUDE3_DEPTH_BACK)):
        Polygon((-20, 62.720286162), (-20, 24.157412536), (-15, 24.157412536), (-15, 17.720286162), (15, 17.720286162), (15, 24.157412536), (20, 24.157412536), (20, 62.720286162), align=None)
    extrude(amount=CUT_EXTRUDE3_DEPTH + CUT_EXTRUDE3_DEPTH_BACK, mode=Mode.SUBTRACT)


with BuildPart() as cut_extrude3_piece_1:
    # of the separate pieces the step leaves, piece 1, a body of its own (cut_extrude3_pieces)
    add(body_2.part.solids().sort_by_distance((242.501846041, 17.720286162, 15))[0])


with BuildPart() as cut_extrude3_piece_2:
    # of the separate pieces the step leaves, piece 2, a body of its own (cut_extrude3_pieces)
    add(body_2.part.solids().sort_by_distance((242.501846041, 17.720286162, -52.5))[0])


with BuildPart() as cut_extrude4_piece_1:
    # of the separate pieces the step leaves, piece 1, a body of its own (cut_extrude4_pieces)
    add(part.part.solids().sort_by_distance((-220, 76.720286162, 100))[0])

    # Sketch7 → Cut-Extrude5 (cut, two sides: drawn at the far end of the back side and taken through both)
    with BuildSketch(Plane(origin=(0, 0, 0), x_dir=(1, 0, 0), z_dir=(0, 1, 0)).offset(-CUT_EXTRUDE5_DEPTH_BACK)):
        with Locations(Location((217.501846041, -75, 0), (0, 0, 270))):
            Circle(SKETCH7_R)
        with Locations(Location((217.501846041, 75, 0), (0, 0, 180))):
            Circle(SKETCH7_R)
        with Locations(Location((-217.501846041, 75, 0), (0, 0, 270))):
            Circle(SKETCH7_R)
        with Locations(Location((-217.501846041, -75, 0), (0, 0, 117.266044451))):
            Circle(SKETCH7_R)
    extrude(amount=CUT_EXTRUDE5_DEPTH + CUT_EXTRUDE5_DEPTH_BACK, mode=Mode.SUBTRACT)

    # Fillet11
    fillet11_edges = [cut_extrude4_piece_1.edges().sort_by_distance(p)[0] for p in [
        (-242.501846041, 0, 100),
        (242.501846041, 0, -100),
        (242.501846041, 0, 100),
        (-242.501846041, 0, -100),
    ]]
    fillet(fillet11_edges, radius=FILLET11_R)


with BuildPart() as cut_extrude4_piece_2:
    # of the separate pieces the step leaves, piece 2, a body of its own (cut_extrude4_pieces)
    add(part.part.solids().sort_by_distance((0, 17.720286162, -40))[0])


with BuildPart() as cut_extrude4_piece_3:
    # of the separate pieces the step leaves, piece 3, a body of its own (cut_extrude4_pieces)
    add(part.part.solids().sort_by_distance((0, 17.720286162, 60))[0])


with BuildPart() as cut_extrude4_piece_4:
    # of the separate pieces the step leaves, piece 4, a body of its own (cut_extrude4_pieces)
    add(part.part.solids().sort_by_distance((-125, 17.720286162, 10))[0])


with BuildPart() as cut_extrude4_piece_5:
    # of the separate pieces the step leaves, piece 5, a body of its own (cut_extrude4_pieces)
    add(part.part.solids().sort_by_distance((115, 17.720286162, 0))[0])


with BuildPart() as body_8:
    # Sketch6 → Boss-Extrude5 (new, two sides: drawn at the far end of the back side and taken through both)
    with BuildSketch(Plane(origin=(0, 0, 0), x_dir=(1, 0, 0), z_dir=(0, 1, 0)).offset(-BOSS_EXTRUDE5_DEPTH_BACK)):
        with BuildLine():
            Line((-247.501846041, 20), (-265.501846041, 20))
            ThreePointArc((-265.501846041, 20), (-266.916059604, 19.414213562), (-267.501846041, 18))
            Line((-267.501846041, 18), (-267.501846041, -18))
            ThreePointArc((-267.501846041, -18), (-266.916059604, -19.414213562), (-265.501846041, -20))
            Line((-265.501846041, -20), (-247.501846041, -20))
            ThreePointArc((-247.501846041, -20), (-243.966312135, -21.464466094), (-242.501846041, -25))
            Line((-242.501846041, -25), (-242.501846041, 25))
            ThreePointArc((-242.501846041, 25), (-243.966312135, 21.464466094), (-247.501846041, 20))
        make_face()
    extrude(amount=BOSS_EXTRUDE5_DEPTH + BOSS_EXTRUDE5_DEPTH_BACK)


with BuildPart() as body_9:
    # Sketch6 → Boss-Extrude5 2 (new, two sides: drawn at the far end of the back side and taken through both)
    with BuildSketch(Plane(origin=(0, 0, 0), x_dir=(1, 0, 0), z_dir=(0, 1, 0)).offset(-BOSS_EXTRUDE5_2_DEPTH_BACK)):
        with BuildLine():
            Line((25, 100), (-25, 100))
            ThreePointArc((-25, 100), (-21.464466094, 101.464466094), (-20, 105))
            Line((-20, 105), (-20, 123))
            ThreePointArc((-20, 123), (-19.414213562, 124.414213562), (-18, 125))
            Line((-18, 125), (18, 125))
            ThreePointArc((18, 125), (19.414213562, 124.414213562), (20, 123))
            Line((20, 123), (20, 105))
            ThreePointArc((20, 105), (21.464466094, 101.464466094), (25, 100))
        make_face()
    extrude(amount=BOSS_EXTRUDE5_2_DEPTH + BOSS_EXTRUDE5_2_DEPTH_BACK)


with BuildPart() as body_10:
    # Sketch6 → Boss-Extrude5 3 (new, two sides: drawn at the far end of the back side and taken through both)
    with BuildSketch(Plane(origin=(0, 0, 0), x_dir=(1, 0, 0), z_dir=(0, 1, 0)).offset(-BOSS_EXTRUDE5_3_DEPTH_BACK)):
        with BuildLine():
            Line((20, -105), (20, -123))
            ThreePointArc((20, -123), (19.414213562, -124.414213562), (18, -125))
            Line((18, -125), (-18, -125))
            ThreePointArc((-18, -125), (-19.414213562, -124.414213562), (-20, -123))
            Line((-20, -123), (-20, -105))
            ThreePointArc((-20, -105), (-21.464466094, -101.464466094), (-25, -100))
            Line((-25, -100), (25, -100))
            ThreePointArc((25, -100), (21.464466094, -101.464466094), (20, -105))
        make_face()
    extrude(amount=BOSS_EXTRUDE5_3_DEPTH + BOSS_EXTRUDE5_3_DEPTH_BACK)


solid = Compound([cut_extrude3_piece_1.part, cut_extrude3_piece_2.part, cut_extrude4_piece_1.part, cut_extrude4_piece_2.part, cut_extrude4_piece_3.part, cut_extrude4_piece_4.part, cut_extrude4_piece_5.part, body_8.part, body_9.part, body_10.part])
